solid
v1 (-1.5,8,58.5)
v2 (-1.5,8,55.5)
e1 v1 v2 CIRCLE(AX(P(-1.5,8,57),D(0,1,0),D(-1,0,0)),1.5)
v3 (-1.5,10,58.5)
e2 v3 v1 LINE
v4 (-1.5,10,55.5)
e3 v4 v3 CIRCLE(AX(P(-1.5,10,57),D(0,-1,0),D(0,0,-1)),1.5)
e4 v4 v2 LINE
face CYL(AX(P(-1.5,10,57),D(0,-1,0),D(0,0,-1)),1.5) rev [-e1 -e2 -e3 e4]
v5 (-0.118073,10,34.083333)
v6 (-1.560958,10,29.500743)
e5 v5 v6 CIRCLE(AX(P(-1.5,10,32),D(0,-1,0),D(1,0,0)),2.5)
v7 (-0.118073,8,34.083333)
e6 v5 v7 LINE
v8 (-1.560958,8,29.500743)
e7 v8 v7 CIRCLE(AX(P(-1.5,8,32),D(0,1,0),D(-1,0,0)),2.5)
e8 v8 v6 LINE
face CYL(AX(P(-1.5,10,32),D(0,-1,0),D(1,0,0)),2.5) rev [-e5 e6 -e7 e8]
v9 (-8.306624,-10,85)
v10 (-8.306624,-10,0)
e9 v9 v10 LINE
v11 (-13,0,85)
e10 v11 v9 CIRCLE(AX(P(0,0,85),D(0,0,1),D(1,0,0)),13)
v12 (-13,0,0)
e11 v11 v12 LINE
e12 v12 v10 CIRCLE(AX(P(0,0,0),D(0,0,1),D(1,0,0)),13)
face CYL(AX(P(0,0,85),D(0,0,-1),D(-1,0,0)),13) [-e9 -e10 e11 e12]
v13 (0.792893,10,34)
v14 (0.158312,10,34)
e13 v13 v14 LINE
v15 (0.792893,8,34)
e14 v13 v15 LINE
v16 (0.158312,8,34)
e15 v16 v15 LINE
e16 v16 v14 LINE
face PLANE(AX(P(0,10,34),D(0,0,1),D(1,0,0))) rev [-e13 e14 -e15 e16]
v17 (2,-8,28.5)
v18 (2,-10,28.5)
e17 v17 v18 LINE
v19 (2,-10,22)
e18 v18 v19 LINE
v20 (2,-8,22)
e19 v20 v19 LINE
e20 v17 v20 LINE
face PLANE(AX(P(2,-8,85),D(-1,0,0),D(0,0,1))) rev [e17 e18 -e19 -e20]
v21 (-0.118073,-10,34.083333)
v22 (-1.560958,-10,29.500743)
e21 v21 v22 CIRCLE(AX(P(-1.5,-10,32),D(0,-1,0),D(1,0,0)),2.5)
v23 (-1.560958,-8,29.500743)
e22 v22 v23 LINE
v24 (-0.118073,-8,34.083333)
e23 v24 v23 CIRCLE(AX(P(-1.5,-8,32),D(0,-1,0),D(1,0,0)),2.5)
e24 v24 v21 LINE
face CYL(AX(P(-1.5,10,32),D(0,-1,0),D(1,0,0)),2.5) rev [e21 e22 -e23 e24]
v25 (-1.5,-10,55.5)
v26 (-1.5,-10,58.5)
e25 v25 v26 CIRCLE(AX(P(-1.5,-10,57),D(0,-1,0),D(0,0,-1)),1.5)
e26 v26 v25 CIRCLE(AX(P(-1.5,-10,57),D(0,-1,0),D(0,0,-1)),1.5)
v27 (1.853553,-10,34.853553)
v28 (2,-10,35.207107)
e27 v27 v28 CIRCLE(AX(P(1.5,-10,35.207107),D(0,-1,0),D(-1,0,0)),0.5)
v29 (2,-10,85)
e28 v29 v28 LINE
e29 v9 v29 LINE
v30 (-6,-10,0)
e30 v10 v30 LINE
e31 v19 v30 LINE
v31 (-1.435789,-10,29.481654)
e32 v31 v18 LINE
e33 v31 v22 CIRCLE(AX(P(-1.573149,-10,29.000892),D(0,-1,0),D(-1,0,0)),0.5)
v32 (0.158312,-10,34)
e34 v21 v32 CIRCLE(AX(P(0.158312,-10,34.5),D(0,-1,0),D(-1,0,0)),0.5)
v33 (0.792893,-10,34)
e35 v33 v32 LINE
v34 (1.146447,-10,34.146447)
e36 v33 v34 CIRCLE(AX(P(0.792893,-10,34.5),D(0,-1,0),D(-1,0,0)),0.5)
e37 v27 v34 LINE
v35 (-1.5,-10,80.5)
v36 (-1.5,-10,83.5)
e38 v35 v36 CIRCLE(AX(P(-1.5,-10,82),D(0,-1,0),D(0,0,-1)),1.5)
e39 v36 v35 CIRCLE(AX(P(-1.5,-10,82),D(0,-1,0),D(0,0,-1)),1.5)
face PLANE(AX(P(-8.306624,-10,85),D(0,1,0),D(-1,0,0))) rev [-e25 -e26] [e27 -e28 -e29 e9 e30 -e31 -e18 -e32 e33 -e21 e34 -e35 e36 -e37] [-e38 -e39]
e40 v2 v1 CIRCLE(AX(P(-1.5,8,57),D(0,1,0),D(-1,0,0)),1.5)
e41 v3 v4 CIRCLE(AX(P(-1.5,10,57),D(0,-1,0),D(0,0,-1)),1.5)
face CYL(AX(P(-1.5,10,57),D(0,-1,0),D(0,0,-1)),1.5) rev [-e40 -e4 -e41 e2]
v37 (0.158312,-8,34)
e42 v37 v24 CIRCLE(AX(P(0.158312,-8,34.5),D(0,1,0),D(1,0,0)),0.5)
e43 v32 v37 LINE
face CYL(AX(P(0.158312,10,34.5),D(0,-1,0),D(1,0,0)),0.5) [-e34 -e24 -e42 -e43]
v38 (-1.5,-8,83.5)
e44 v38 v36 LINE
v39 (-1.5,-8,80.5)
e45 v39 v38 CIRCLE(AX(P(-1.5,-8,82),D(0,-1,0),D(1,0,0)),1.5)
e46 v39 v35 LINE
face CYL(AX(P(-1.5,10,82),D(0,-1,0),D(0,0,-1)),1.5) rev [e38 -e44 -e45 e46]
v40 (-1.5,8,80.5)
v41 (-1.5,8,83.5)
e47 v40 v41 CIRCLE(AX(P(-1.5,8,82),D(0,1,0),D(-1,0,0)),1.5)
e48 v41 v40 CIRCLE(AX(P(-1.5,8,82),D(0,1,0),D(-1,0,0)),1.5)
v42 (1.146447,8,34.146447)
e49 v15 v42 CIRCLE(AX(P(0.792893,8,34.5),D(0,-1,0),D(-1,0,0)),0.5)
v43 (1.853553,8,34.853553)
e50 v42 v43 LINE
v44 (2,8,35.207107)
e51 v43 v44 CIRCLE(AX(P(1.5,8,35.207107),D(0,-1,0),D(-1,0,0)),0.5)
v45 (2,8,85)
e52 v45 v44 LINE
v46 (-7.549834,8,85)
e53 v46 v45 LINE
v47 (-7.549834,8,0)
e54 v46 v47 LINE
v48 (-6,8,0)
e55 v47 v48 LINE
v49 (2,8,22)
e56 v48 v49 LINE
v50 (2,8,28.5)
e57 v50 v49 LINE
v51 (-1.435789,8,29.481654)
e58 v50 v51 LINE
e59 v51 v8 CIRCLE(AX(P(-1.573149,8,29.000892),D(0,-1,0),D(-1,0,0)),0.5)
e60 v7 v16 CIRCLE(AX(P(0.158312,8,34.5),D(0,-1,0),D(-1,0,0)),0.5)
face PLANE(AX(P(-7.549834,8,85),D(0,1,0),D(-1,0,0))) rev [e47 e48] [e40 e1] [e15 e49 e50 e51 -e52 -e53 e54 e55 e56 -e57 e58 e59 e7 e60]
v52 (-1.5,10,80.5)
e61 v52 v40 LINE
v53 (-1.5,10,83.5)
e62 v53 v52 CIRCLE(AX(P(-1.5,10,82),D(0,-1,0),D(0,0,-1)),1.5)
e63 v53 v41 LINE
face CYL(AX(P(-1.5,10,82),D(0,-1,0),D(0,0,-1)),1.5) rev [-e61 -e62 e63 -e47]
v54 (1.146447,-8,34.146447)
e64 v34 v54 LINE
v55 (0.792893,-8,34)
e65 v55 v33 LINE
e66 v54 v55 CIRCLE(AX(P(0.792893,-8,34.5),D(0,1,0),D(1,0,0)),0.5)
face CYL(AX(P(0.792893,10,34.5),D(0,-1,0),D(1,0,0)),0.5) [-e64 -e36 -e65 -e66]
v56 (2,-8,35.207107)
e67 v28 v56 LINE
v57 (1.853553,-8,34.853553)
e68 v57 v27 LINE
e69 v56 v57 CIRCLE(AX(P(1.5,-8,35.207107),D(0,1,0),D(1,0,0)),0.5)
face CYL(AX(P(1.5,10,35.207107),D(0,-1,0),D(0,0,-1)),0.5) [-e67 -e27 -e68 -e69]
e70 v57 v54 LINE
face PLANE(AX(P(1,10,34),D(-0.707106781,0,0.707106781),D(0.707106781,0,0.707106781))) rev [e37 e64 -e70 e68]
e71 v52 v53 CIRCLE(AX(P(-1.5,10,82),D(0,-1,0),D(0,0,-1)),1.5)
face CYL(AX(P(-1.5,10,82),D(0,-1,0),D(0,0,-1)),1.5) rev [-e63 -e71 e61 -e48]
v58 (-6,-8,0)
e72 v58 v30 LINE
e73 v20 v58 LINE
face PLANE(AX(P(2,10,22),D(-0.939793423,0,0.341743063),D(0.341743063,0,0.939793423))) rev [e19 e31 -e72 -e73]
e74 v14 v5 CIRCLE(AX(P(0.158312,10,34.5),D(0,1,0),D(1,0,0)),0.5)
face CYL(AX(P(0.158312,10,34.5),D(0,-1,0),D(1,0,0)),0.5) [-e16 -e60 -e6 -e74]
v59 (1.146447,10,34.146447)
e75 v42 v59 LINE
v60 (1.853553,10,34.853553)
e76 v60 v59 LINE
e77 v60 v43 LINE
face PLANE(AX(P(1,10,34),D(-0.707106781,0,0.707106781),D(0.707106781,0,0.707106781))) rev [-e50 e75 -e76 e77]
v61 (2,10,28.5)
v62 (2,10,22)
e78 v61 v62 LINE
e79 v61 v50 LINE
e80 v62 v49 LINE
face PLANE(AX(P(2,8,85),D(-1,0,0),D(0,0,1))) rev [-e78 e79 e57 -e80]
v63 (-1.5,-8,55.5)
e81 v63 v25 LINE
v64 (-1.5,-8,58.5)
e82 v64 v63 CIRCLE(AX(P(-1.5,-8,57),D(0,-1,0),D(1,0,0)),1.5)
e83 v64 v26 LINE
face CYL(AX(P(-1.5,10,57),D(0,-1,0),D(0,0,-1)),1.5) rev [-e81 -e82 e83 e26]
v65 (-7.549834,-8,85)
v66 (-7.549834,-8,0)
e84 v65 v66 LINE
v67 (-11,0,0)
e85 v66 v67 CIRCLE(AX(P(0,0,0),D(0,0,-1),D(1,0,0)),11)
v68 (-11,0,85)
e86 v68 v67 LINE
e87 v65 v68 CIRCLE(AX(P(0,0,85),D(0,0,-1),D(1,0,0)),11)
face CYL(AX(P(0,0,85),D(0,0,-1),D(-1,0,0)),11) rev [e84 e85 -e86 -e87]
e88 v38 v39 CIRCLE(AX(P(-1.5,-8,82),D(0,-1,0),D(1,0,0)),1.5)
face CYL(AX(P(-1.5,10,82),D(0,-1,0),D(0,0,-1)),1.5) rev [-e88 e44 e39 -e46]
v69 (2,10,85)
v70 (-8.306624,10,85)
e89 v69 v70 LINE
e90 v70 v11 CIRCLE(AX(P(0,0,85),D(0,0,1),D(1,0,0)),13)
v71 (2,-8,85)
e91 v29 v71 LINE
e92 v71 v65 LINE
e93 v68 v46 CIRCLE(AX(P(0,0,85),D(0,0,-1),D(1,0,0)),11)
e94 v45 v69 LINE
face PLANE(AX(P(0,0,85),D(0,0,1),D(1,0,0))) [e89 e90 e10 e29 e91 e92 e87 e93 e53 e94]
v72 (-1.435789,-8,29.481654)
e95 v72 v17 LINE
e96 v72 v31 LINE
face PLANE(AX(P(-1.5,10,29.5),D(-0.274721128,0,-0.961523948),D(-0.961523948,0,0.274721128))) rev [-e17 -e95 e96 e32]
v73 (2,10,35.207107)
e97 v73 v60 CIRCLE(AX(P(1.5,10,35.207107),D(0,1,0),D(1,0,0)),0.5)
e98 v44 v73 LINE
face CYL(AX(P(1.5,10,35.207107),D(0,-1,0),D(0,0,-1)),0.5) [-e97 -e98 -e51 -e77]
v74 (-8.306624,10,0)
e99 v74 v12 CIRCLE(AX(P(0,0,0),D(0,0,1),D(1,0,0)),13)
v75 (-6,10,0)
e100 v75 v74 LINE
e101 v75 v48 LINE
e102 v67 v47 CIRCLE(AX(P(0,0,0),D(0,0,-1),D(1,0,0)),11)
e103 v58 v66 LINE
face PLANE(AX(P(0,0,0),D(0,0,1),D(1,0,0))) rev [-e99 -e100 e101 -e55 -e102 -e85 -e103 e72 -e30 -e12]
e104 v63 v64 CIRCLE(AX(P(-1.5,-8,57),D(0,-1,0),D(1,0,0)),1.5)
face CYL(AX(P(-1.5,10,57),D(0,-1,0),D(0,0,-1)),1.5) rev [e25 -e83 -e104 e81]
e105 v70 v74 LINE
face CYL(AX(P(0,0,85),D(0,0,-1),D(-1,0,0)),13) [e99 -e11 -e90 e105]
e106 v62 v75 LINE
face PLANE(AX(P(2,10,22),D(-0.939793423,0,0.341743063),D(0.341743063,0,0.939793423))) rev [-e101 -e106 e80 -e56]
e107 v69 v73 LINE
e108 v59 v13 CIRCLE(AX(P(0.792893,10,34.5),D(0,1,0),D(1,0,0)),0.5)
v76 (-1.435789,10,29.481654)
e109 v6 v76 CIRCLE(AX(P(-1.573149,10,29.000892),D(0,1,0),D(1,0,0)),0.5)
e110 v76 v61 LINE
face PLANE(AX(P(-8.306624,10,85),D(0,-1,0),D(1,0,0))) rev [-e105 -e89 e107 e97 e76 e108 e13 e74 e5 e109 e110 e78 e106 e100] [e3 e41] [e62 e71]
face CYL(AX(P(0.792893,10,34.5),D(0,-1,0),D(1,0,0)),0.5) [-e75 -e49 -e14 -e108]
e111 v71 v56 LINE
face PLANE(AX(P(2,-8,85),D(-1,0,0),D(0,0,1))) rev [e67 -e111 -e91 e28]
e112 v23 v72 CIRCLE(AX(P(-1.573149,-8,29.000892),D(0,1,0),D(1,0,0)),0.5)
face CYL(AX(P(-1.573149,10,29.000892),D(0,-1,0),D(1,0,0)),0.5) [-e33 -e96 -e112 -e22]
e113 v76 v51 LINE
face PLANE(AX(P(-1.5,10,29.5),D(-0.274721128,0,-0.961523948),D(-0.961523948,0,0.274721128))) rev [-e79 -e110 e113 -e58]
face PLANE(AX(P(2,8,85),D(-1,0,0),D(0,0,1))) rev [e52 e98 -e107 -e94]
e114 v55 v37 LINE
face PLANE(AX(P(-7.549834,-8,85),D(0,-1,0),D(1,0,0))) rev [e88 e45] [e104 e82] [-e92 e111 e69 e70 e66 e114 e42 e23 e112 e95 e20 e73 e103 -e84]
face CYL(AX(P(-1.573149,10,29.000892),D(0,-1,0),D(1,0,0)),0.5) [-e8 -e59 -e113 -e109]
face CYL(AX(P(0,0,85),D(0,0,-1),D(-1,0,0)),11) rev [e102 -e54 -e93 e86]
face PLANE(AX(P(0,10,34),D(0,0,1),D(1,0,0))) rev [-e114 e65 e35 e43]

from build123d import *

# Parameters (mm, degrees)
BOSS_EXTRUDE1_DEPTH = 85
SKETCH2_R           = 1.5
CUT_EXTRUDE1_DEPTH  = 89.283633817
CUT_EXTRUDE2_DEPTH  = 89.283633817
FILLET1_R           = 0.5
FILLET2_R           = 0.5


with BuildPart() as part:
    # Sketch1 → Boss-Extrude1 (new body)
    with BuildSketch(Plane.XY):
        with BuildLine():
            Line((-8.306623863, 10), (2, 10))
            Line((2, 10), (2, 8))
            Line((2, 8), (-7.549834435, 8))
            ThreePointArc((-7.549834435, 8), (-11, 0), (-7.549834435, -8))
            Line((-7.549834435, -8), (2, -8))
            Line((2, -8), (2, -10))
            Line((2, -10), (-8.306623863, -10))
            ThreePointArc((-8.306623863, -10), (-13, 0), (-8.306623863, 10))
        make_face()
    extrude(amount=BOSS_EXTRUDE1_DEPTH)

    # Sketch2 → Cut-Extrude1 (cut, through all)
    with BuildSketch(Plane(origin=(0, -10, 0), x_dir=(-1, 0, 0), z_dir=(0, -1, 0))):
        with Locations(Location((1.5, -82, 0), (0, 0, 90))):
            Circle(SKETCH2_R)
        with Locations(Location((1.5, -57, 0), (0, 0, 90))):
            Circle(SKETCH2_R)
        Polygon((-2, -22), (6, 0), (-2, 0), align=None)
    extrude(amount=-CUT_EXTRUDE1_DEPTH, mode=Mode.SUBTRACT)

    # Sketch3 → Cut-Extrude2 (cut, through all)
    with BuildSketch(Plane(origin=(0, -10, 0), x_dir=(-1, 0, 0), z_dir=(0, -1, 0))):
        with BuildLine():
            Line((-2, -28.5), (-2, -35))
            Line((-2, -35), (-1, -34))
            Line((-1, -34), (0, -34))
            ThreePointArc((0, -34), (3.871708245, -32.790569415), (1.5, -29.5))
            Line((1.5, -29.5), (-2, -28.5))
        make_face()
    extrude(amount=-CUT_EXTRUDE2_DEPTH, mode=Mode.SUBTRACT)

    # Fillet1
    fillet1_edges = [part.edges().sort_by_distance(p)[0] for p in [
        (1, -9, 34),
        (1, 9, 34),
        (2, -9, 35),
        (2, 9, 35),
        (0, -9, 34),
        (0, 9, 34),
    ]]
    fillet(fillet1_edges, radius=FILLET1_R)

    # Fillet2
    fillet2_edges = [part.edges().sort_by_distance(p)[0] for p in [
        (-1.5, -9, 29.5),
        (-1.5, 9, 29.5),
    ]]
    fillet(fillet2_edges, radius=FILLET2_R)


solid = part.part
